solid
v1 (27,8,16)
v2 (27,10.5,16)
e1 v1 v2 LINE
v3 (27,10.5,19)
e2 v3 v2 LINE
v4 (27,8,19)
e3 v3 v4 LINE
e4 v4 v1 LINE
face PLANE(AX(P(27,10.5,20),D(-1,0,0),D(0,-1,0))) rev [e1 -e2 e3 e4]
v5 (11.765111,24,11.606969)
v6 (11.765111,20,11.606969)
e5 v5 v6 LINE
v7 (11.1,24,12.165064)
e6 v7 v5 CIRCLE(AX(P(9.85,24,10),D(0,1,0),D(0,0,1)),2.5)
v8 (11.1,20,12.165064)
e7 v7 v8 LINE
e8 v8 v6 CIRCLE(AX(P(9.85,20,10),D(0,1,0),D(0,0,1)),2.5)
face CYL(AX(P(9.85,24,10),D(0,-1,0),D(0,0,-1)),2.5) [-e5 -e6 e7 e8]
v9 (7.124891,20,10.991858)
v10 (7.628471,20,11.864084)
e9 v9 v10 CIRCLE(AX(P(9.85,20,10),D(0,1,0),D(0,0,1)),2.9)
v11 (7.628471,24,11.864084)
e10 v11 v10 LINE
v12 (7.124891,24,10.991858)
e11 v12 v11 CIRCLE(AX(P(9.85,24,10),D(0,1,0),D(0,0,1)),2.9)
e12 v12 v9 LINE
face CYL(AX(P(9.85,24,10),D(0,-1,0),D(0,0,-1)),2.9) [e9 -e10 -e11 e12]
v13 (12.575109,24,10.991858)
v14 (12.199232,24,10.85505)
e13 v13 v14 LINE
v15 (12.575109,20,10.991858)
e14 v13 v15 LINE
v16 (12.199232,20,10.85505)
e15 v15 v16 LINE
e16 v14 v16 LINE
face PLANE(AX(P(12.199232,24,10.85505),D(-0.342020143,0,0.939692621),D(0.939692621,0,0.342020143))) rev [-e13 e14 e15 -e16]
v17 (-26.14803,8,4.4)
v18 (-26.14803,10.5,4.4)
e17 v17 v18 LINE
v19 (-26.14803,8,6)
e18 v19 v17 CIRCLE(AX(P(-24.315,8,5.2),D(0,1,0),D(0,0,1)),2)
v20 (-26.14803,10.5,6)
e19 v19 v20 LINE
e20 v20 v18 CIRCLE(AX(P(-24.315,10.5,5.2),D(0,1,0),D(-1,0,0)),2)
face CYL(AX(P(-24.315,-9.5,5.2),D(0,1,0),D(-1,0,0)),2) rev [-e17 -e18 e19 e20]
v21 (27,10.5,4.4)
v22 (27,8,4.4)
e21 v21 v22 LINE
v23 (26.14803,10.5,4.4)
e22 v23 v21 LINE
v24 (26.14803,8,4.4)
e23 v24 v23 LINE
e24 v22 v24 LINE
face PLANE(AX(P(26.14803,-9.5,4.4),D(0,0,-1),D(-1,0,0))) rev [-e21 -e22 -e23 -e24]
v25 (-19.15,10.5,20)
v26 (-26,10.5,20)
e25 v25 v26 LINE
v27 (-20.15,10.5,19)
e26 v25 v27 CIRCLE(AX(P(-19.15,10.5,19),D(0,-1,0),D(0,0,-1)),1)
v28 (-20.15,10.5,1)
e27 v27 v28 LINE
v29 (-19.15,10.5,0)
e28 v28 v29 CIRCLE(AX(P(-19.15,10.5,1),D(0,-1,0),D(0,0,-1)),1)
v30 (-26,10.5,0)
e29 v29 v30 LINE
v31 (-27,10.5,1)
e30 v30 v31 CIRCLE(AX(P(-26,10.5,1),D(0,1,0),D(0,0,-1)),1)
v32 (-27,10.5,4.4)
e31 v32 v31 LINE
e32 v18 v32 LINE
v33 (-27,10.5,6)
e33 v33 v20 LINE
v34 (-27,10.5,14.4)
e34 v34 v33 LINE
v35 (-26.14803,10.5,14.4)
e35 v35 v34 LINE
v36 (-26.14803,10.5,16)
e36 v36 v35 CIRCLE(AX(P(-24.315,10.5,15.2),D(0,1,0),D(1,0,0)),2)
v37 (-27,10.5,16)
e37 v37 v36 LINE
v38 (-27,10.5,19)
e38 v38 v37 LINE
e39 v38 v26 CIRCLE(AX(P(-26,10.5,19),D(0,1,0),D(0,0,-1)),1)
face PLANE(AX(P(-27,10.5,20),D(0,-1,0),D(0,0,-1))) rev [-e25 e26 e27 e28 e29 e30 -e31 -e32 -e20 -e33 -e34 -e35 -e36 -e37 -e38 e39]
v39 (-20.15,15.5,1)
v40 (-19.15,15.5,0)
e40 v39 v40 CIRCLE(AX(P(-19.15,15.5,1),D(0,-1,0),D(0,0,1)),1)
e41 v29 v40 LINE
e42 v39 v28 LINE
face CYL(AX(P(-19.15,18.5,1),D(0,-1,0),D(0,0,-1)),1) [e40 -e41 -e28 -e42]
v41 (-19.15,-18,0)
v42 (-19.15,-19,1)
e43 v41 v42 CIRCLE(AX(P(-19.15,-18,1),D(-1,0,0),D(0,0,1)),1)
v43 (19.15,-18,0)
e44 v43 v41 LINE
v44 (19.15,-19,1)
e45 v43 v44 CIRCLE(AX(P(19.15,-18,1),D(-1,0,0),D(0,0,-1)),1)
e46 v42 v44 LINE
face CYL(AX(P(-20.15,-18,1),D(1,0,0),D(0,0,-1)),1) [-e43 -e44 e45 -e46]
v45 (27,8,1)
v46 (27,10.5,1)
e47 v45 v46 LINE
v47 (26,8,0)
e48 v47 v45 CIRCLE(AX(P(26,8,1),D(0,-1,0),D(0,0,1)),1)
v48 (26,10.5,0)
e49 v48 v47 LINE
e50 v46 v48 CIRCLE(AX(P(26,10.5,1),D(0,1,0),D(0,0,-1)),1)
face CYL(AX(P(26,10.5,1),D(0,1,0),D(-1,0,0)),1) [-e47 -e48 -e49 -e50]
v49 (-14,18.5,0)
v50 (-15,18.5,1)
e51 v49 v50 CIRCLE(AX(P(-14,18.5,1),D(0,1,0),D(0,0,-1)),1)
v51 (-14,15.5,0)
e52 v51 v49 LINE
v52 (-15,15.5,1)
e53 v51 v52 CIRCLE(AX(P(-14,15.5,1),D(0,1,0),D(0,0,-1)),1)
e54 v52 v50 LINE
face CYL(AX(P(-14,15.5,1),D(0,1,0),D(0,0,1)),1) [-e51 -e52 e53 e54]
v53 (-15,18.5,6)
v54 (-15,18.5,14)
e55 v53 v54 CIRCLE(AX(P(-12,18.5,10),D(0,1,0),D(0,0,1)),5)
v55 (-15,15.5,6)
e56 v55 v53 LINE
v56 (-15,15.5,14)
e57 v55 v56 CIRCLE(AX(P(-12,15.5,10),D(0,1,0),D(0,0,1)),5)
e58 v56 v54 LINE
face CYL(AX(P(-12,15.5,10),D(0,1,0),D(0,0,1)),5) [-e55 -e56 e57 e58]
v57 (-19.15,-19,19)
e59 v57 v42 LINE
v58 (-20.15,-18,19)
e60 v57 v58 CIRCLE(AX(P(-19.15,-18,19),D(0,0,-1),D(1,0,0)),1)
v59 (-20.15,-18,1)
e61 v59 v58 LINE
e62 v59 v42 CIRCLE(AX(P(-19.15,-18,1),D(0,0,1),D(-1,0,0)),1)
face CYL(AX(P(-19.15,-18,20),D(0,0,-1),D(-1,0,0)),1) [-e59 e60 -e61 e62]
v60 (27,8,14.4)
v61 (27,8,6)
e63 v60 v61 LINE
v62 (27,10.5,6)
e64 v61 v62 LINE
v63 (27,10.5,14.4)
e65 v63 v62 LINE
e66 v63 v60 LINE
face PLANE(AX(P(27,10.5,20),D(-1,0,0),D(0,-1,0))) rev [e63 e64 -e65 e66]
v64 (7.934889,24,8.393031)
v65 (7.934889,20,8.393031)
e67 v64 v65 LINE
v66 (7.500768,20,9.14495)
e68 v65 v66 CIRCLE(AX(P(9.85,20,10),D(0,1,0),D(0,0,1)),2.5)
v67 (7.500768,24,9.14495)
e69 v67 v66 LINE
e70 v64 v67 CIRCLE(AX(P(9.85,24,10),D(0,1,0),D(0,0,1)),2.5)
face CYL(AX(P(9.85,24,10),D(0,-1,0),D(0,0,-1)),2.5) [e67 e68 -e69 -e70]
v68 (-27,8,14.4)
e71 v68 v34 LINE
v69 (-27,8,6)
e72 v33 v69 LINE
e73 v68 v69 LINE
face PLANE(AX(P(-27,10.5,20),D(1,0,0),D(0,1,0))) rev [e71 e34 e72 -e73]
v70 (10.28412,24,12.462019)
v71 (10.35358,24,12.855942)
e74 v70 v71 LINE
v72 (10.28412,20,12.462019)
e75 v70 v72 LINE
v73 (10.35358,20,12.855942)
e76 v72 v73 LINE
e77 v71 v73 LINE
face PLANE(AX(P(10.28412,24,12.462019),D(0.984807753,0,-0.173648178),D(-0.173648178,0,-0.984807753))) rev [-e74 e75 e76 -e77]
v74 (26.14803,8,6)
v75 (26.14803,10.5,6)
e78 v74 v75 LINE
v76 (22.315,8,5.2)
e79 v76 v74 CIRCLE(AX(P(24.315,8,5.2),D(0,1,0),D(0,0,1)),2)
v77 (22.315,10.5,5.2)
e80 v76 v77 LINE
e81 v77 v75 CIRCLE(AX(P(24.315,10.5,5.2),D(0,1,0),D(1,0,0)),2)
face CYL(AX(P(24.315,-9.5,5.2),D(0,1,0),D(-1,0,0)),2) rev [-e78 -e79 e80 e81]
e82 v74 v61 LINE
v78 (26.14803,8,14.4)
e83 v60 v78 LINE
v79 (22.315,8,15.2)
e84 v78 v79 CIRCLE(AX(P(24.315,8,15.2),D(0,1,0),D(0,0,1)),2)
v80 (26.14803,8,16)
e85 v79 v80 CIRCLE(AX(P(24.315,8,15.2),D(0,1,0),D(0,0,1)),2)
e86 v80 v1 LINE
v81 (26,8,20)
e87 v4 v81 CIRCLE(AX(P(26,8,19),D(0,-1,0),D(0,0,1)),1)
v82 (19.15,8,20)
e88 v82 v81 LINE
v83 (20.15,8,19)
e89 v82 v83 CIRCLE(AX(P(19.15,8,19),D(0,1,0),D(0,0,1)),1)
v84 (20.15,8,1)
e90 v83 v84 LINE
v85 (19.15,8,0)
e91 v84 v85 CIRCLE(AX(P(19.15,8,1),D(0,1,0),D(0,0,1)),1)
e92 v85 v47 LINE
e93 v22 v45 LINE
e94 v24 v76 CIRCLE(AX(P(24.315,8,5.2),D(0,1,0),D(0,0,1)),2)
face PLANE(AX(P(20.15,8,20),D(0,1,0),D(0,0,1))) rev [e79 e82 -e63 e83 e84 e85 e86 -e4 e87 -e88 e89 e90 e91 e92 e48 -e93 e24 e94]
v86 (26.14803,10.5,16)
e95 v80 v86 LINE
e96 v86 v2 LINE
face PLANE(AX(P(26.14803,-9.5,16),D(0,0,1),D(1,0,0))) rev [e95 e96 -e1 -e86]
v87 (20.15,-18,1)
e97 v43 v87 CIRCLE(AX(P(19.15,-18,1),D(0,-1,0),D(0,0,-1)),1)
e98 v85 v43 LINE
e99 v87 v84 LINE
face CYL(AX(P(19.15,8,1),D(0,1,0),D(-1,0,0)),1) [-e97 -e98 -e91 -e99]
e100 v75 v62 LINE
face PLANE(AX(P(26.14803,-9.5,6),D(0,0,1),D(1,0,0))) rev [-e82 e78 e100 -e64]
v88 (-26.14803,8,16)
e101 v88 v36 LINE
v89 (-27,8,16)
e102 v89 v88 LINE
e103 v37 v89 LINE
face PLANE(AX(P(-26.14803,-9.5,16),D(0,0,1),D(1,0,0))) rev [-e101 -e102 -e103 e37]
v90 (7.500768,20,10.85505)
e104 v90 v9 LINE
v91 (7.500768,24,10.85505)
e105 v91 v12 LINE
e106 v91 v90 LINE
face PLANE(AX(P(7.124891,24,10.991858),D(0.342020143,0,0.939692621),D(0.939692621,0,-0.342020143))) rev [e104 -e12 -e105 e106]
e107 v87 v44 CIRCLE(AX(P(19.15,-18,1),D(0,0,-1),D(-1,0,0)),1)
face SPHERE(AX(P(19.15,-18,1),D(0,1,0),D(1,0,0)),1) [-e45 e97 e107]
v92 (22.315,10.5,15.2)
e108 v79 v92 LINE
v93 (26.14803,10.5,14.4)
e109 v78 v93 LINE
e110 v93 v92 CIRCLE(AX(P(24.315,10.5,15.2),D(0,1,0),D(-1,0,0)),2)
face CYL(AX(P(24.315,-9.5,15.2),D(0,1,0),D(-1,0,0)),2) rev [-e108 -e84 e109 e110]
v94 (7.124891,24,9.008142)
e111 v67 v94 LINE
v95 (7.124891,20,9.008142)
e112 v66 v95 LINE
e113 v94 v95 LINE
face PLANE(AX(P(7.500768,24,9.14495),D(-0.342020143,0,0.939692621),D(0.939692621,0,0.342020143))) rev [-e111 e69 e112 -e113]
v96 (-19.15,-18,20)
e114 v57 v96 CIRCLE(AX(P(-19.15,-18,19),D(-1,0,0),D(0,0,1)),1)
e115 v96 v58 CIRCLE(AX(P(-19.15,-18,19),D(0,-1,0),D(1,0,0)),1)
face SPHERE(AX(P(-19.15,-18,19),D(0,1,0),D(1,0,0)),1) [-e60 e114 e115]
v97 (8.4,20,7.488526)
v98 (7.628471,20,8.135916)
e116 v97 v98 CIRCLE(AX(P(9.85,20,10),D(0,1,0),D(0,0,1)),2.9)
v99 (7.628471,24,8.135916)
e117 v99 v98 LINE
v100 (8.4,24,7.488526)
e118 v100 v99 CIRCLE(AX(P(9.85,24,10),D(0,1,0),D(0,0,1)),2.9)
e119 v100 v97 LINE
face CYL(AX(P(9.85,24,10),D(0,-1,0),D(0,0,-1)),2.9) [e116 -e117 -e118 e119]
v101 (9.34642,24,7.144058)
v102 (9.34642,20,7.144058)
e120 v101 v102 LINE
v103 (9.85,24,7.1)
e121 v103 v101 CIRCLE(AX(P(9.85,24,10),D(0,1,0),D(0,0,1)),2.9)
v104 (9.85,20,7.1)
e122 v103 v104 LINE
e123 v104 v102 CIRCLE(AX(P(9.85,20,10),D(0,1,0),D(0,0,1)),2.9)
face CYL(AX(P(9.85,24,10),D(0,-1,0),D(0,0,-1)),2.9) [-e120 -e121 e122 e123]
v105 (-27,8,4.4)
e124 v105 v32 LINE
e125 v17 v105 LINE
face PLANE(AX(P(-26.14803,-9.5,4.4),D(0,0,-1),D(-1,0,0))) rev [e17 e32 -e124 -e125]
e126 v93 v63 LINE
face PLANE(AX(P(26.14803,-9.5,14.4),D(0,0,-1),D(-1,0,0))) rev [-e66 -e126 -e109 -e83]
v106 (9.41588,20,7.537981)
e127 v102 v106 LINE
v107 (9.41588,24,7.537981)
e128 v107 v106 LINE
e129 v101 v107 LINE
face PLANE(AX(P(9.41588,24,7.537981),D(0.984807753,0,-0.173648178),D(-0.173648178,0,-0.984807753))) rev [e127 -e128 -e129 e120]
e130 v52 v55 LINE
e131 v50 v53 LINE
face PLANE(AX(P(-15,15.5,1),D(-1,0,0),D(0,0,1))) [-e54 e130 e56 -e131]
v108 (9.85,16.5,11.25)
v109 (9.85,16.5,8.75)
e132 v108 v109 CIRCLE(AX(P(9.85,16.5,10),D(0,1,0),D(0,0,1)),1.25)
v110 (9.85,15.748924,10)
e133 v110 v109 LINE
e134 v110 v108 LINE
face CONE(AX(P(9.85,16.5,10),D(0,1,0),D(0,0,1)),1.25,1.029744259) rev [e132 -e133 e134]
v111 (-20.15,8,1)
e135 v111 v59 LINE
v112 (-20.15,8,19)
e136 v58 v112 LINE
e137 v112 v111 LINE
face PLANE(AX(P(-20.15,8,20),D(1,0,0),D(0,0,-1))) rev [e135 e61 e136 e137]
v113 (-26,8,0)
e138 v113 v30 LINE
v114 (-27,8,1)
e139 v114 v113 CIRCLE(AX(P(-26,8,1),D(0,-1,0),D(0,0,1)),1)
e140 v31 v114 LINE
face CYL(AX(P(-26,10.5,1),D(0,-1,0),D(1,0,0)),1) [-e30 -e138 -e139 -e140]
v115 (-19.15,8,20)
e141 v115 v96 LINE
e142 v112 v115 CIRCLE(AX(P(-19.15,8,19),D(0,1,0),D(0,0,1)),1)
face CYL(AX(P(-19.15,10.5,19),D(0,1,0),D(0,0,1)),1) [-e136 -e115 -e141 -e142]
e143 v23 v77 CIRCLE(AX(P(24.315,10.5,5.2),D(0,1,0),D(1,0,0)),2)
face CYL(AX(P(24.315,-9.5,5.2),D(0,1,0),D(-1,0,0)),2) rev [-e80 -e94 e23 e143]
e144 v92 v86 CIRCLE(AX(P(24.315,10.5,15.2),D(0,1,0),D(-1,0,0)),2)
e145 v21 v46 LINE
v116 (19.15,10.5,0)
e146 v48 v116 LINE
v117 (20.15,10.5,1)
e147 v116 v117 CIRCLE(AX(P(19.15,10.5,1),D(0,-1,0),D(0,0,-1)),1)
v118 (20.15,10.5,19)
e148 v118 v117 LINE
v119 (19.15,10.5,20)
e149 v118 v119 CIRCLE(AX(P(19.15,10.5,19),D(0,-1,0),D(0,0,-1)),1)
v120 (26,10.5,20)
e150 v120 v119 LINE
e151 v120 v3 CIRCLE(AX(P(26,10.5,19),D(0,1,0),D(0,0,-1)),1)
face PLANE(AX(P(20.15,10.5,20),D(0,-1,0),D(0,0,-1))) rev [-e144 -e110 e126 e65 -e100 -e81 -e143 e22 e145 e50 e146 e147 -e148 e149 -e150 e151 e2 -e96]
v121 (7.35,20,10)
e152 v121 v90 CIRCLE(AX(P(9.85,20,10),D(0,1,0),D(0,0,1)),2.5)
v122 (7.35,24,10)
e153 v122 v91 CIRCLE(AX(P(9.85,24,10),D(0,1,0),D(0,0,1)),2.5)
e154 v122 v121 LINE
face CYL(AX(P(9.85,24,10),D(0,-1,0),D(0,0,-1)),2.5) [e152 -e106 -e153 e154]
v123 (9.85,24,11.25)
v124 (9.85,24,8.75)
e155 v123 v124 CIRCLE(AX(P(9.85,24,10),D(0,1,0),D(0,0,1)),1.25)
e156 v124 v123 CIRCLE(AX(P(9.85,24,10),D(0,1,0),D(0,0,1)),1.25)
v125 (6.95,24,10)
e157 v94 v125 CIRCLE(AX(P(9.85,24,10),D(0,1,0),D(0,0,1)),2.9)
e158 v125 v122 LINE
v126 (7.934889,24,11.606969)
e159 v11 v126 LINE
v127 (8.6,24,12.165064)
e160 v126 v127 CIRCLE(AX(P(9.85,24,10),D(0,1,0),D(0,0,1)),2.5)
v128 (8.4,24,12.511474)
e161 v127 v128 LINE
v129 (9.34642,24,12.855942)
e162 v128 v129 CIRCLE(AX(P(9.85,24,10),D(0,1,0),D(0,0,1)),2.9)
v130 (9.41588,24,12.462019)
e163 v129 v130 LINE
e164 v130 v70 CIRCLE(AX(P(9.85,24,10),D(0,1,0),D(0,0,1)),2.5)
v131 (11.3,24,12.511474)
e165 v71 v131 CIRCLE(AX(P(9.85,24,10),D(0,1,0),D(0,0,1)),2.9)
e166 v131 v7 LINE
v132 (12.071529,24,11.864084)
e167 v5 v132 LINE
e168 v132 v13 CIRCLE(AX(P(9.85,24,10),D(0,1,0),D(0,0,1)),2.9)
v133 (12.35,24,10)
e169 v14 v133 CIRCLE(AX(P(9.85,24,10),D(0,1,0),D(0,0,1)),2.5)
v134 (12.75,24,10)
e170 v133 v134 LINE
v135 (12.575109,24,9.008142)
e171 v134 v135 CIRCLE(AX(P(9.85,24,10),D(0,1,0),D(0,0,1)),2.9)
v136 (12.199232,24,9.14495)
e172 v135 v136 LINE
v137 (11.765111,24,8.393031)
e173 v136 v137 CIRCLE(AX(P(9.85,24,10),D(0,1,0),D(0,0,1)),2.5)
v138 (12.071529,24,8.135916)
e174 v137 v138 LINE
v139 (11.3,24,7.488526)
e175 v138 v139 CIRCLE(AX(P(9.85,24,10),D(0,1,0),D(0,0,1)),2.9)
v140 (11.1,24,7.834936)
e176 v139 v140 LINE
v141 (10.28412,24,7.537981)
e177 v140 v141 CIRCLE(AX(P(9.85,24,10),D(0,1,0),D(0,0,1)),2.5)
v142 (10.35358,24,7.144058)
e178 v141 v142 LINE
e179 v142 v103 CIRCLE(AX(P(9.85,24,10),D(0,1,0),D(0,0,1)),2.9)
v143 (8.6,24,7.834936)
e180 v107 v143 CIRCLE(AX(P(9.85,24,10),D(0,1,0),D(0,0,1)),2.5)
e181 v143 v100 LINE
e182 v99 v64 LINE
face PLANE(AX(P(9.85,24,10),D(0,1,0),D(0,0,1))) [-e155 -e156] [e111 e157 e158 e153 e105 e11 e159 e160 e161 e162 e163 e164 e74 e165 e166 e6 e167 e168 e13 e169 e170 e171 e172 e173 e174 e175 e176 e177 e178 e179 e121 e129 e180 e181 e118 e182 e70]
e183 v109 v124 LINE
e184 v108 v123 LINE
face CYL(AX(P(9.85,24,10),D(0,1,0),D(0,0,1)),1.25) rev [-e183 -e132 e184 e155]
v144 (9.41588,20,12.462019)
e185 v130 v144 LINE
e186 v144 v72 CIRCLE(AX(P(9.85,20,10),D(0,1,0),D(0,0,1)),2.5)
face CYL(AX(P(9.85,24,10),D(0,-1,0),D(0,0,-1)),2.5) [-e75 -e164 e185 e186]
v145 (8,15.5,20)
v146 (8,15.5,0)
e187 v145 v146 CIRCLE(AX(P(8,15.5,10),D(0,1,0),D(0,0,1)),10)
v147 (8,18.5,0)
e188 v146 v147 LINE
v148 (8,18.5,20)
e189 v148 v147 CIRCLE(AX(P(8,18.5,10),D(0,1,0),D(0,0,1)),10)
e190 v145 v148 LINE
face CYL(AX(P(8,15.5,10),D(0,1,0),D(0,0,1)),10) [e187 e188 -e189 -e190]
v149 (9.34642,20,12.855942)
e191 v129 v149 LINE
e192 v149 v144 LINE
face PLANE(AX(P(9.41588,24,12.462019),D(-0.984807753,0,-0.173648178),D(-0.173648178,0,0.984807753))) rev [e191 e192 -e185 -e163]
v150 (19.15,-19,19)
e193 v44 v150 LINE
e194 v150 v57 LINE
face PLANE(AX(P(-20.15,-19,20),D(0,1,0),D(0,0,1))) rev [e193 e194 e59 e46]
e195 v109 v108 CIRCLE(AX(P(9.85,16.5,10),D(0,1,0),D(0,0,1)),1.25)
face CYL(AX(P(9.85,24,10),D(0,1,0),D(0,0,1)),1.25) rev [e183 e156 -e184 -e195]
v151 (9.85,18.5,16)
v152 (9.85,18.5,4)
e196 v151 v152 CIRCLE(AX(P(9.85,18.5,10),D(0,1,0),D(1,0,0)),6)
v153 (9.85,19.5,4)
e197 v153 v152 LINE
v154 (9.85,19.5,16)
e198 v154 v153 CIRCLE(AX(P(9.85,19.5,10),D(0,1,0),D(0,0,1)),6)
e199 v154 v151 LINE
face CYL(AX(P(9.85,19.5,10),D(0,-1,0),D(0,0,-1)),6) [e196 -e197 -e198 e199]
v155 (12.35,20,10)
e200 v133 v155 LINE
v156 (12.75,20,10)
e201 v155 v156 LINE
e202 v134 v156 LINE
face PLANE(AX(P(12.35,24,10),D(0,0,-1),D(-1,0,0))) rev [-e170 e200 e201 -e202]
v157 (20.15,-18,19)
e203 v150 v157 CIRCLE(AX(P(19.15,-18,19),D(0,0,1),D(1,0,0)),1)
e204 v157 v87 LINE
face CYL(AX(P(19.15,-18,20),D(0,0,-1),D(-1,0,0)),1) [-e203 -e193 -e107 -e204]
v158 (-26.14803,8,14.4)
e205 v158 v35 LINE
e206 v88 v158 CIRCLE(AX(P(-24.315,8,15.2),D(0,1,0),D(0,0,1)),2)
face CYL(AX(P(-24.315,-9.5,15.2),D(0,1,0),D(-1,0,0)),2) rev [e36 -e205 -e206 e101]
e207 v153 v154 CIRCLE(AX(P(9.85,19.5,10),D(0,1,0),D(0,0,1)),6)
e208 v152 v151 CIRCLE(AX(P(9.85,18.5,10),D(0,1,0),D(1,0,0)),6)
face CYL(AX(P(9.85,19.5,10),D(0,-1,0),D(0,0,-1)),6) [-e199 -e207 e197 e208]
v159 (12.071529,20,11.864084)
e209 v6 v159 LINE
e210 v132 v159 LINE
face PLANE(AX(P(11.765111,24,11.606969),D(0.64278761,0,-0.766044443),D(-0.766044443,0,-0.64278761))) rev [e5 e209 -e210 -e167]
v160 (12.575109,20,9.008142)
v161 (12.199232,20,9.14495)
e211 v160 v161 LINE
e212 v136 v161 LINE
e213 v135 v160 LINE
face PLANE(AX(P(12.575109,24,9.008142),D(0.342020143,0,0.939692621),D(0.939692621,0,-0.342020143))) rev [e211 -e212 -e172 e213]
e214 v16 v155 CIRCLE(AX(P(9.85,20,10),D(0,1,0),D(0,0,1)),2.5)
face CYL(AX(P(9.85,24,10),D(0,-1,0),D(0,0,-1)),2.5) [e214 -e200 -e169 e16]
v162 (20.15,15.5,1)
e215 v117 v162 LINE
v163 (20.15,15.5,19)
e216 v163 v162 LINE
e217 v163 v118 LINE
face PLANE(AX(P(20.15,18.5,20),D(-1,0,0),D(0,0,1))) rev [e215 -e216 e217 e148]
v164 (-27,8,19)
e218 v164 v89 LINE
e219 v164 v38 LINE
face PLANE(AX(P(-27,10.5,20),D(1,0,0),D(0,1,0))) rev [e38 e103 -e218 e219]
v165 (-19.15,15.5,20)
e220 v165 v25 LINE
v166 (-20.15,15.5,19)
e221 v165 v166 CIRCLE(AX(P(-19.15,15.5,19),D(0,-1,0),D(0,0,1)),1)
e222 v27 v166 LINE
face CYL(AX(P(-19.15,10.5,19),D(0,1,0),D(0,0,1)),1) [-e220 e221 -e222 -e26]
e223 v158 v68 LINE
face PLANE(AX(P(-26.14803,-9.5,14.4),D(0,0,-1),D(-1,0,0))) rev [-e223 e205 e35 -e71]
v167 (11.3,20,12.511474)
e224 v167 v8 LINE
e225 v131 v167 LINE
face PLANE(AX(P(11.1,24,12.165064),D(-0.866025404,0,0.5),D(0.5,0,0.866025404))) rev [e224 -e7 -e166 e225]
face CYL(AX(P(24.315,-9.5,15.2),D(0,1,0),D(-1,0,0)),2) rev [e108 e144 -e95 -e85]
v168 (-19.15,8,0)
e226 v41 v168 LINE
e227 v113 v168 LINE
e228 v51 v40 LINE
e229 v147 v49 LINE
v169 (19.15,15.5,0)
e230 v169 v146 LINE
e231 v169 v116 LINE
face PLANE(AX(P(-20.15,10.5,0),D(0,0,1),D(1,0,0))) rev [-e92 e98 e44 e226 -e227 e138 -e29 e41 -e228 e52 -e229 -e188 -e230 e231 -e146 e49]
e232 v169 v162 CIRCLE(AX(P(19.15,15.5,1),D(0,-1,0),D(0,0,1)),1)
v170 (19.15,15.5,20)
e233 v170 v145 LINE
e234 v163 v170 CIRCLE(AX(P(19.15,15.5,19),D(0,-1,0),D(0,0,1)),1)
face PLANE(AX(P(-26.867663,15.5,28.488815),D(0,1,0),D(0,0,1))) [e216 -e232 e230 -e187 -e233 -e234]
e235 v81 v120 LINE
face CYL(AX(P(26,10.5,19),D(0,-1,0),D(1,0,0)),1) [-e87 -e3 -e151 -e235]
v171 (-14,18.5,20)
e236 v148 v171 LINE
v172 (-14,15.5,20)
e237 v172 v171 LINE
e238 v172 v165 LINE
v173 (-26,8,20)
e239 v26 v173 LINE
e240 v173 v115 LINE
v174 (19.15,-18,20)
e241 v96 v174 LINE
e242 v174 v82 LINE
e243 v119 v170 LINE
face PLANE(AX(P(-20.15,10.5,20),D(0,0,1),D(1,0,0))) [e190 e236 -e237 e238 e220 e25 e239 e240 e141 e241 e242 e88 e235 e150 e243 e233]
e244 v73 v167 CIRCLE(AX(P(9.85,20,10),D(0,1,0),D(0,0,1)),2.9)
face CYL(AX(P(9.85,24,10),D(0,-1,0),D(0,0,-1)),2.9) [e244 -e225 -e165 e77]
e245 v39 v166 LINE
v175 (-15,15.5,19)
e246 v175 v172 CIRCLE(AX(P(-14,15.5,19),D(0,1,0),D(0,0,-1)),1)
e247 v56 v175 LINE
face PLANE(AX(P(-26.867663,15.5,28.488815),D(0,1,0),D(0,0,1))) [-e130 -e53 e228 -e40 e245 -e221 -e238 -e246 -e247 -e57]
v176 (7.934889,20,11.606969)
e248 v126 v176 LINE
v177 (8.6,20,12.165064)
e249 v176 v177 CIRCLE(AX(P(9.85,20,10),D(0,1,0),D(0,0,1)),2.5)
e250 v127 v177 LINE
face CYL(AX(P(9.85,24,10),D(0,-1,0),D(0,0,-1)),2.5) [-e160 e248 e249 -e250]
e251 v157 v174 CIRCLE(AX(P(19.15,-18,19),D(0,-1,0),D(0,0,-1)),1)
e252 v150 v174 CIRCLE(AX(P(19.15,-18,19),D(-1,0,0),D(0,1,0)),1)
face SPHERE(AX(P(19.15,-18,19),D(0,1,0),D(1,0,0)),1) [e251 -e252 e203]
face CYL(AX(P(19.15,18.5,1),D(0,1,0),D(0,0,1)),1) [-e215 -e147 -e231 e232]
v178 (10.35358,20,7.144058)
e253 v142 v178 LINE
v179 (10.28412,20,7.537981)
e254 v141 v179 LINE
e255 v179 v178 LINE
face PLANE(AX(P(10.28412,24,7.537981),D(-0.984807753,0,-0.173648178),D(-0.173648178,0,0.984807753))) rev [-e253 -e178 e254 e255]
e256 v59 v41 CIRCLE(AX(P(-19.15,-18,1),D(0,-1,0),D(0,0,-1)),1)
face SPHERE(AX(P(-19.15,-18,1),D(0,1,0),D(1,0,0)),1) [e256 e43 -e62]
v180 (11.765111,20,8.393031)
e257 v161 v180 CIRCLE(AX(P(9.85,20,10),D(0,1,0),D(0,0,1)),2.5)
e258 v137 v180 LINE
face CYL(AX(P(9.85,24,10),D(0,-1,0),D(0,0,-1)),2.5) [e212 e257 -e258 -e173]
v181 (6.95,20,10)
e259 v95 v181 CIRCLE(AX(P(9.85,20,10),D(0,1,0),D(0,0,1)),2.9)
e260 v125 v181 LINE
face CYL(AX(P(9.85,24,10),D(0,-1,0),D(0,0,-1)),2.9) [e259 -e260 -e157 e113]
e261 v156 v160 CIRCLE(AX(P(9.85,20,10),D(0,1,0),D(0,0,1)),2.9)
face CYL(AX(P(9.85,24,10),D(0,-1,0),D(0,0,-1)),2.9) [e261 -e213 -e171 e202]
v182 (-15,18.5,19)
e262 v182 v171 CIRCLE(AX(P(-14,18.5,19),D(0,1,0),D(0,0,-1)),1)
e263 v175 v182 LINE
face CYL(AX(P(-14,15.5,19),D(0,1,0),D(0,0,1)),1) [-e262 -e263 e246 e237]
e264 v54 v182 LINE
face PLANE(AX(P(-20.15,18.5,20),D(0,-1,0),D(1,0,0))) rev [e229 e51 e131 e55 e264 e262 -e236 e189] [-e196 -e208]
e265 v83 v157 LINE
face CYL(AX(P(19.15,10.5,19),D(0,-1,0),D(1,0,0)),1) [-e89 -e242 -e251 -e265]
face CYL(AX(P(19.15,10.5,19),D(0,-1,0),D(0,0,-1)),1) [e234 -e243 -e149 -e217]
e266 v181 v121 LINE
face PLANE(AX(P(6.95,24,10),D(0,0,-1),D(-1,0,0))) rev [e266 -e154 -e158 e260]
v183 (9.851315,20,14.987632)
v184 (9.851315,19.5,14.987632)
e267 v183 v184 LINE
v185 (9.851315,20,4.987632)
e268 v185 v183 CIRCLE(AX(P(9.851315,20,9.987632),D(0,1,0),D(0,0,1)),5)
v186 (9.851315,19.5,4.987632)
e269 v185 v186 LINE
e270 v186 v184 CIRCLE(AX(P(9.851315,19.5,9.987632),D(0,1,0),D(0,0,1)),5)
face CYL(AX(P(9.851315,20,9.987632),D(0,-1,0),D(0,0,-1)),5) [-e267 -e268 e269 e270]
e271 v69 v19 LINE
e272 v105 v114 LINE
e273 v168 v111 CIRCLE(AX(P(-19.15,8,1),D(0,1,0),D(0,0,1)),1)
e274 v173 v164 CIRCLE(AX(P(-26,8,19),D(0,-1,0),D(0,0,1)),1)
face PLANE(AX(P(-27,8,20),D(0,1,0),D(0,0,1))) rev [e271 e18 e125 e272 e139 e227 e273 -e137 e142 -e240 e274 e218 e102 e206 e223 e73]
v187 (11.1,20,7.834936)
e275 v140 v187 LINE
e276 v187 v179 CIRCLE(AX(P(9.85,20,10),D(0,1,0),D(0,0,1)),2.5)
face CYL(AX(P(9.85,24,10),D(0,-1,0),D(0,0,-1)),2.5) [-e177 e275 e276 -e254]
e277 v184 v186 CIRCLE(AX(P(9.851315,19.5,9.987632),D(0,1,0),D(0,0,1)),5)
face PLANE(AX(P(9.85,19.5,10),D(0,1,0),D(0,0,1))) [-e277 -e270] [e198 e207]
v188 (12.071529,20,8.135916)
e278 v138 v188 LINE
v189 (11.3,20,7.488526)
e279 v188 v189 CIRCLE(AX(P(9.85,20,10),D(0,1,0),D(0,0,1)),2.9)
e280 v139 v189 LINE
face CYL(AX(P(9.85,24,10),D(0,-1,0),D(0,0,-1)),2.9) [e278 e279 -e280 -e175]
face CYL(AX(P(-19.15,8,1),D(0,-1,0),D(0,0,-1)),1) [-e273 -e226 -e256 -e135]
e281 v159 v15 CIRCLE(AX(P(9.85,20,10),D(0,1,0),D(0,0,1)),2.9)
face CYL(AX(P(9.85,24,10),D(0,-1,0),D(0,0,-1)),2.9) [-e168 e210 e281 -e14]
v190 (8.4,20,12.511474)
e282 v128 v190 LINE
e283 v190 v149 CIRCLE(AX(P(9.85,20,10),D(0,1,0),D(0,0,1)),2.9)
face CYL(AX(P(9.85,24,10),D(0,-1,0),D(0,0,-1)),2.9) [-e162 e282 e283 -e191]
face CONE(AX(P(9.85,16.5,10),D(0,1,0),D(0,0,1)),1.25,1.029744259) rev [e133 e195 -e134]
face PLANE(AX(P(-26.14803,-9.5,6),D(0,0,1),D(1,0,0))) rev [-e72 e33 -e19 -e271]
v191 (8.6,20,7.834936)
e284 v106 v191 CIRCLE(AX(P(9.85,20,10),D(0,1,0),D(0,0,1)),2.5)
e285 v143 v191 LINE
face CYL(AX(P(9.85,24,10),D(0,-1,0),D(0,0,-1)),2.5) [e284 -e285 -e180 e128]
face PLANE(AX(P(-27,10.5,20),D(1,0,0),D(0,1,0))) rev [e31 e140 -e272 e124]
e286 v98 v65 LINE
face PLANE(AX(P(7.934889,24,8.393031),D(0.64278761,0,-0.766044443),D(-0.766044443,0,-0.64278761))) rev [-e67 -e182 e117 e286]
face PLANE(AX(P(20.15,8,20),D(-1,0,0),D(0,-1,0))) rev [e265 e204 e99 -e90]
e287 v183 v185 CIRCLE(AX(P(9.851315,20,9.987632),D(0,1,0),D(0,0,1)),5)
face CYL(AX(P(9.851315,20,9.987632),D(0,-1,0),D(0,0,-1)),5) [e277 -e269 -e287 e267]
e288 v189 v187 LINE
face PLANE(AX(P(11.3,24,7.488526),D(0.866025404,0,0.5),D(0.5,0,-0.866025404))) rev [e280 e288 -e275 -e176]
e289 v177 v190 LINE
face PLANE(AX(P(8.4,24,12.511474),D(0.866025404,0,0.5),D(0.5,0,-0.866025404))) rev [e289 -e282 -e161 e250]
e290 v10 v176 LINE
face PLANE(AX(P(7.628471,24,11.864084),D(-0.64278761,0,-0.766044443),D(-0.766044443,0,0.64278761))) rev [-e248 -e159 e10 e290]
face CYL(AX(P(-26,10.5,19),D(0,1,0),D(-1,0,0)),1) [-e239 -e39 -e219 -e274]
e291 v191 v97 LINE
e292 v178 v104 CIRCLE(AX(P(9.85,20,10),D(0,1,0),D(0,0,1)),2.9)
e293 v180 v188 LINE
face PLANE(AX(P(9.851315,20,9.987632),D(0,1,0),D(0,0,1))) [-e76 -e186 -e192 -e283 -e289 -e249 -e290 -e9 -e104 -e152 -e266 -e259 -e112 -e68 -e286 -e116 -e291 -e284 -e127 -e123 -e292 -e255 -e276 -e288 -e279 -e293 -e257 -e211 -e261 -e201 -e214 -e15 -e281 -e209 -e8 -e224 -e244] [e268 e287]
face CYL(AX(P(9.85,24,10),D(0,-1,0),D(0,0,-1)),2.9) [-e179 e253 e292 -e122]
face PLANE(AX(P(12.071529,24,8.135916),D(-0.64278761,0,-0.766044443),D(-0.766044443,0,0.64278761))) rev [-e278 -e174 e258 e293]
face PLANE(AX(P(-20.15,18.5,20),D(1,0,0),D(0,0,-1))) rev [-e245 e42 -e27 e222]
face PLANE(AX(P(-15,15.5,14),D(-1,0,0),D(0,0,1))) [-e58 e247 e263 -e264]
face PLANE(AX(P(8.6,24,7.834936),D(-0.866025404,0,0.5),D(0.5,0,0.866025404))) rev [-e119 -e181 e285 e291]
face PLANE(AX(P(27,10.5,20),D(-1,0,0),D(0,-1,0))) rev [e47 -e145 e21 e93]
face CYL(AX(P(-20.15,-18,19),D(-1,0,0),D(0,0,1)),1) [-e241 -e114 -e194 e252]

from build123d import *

# Parameters (mm, degrees)
BOSS_EXTRUDE1_DEPTH   = 20
FILLET1_R             = 1
CUT_EXTRUDE1_DEPTH    = 20
SKETCH3_W             = 51.867663345
SKETCH3_H             = 35.261757523
CUT_EXTRUDE2_DEPTH    = 3
SKETCH4_R             = 6
BOSS_EXTRUDE2_DEPTH   = 1
SKETCH5_R             = 5
BOSS_EXTRUDE3_DEPTH   = 0.5
SKETCH6_R             = 1
BOSS_EXTRUDE4_DEPTH   = 4
M3_TAPPED_HOLE1_D     = 2.5
M3_TAPPED_HOLE1_DEPTH = 7.5
M3_TAPPED_HOLE1_TIP   = 0.751075774


with BuildPart() as part:
    # Sketch1 → Boss-Extrude1 (new body)
    with BuildSketch(Plane.XY):
        Polygon((20.15, 8), (27, 8), (27, 10.5), (20.15, 10.5), (20.15, 18.5), (-20.15, 18.5), (-20.15, 10.5), (-27, 10.5), (-27, 8), (-20.15, 8), (-20.15, -19), (20.15, -19), align=None)
    extrude(amount=BOSS_EXTRUDE1_DEPTH)

    # Fillet1
    fillet1_edges = [part.edges().sort_by_distance(p)[0] for p in [
        (-27, 9.25, 20),
        (20.15, 14.5, 0),
        (27, 9.25, 0),
        (20.15, -5.5, 0),
        (0, -19, 0),
        (-20.15, -5.5, 0),
        (-27, 9.25, 0),
        (-20.15, 14.5, 0),
        (-20.15, -5.5, 20),
        (0, -19, 20),
        (-20.15, 18.5, 10),
        (20.15, 18.5, 10),
        (20.15, -19, 10),
        (-20.15, -19, 10),
        (20.15, -5.5, 20),
        (27, 9.25, 20),
        (20.15, 14.5, 20),
        (-20.15, 14.5, 20),
    ]]
    fillet(fillet1_edges, radius=FILLET1_R)

    # Sketch2 → Cut-Extrude1 (cut)
    with BuildSketch(Plane(origin=(0, 10.5, 0), x_dir=(1, 0, 0), z_dir=(0, 1, 0))):
        with BuildLine():
            Line((-26.148030278, -4.4), (-29.222738853, -4.4))
            Line((-29.222738853, -4.4), (-29.222738853, -6))
            Line((-29.222738853, -6), (-26.148030278, -6))
            ThreePointArc((-26.148030278, -6), (-22.315, -5.2), (-26.148030278, -4.4))
        make_face()
        with BuildLine():
            Line((-26.148030278, -14.4), (-29.222738853, -14.4))
            Line((-29.222738853, -14.4), (-29.222738853, -16))
            Line((-29.222738853, -16), (-26.148030278, -16))
            ThreePointArc((-26.148030278, -16), (-22.315, -15.2), (-26.148030278, -14.4))
        make_face()
        with BuildLine():
            Line((26.148030278, -16), (29.222738853, -16))
            Line((29.222738853, -16), (29.222738853, -14.4))
            Line((29.222738853, -14.4), (26.148030278, -14.4))
            ThreePointArc((26.148030278, -14.4), (22.315, -15.2), (26.148030278, -16))
        make_face()
        with BuildLine():
            Line((29.222738853, -4.4), (29.222738853, -6))
            Line((29.222738853, -6), (26.148030278, -6))
            ThreePointArc((26.148030278, -6), (22.315, -5.2), (26.148030278, -4.4))
            Line((26.148030278, -4.4), (29.222738853, -4.4))
        make_face()
    extrude(amount=-CUT_EXTRUDE1_DEPTH, mode=Mode.SUBTRACT)

    # Sketch3 → Cut-Extrude2 (cut)
    with BuildSketch(Plane(origin=(0, 18.5, 0), x_dir=(1, 0, 0), z_dir=(0, 1, 0))):
        with Locations((-0.933831673, -10.85793672)):
            Rectangle(SKETCH3_W, SKETCH3_H)
        with BuildLine():
            Line((-14, 0), (8, 0))
            ThreePointArc((8, 0), (18, -10), (8, -20))
            Line((8, -20), (-14, -20))
            ThreePointArc((-14, -20), (-14.707106781, -19.707106781), (-15, -19))
            Line((-15, -19), (-15, -14))
            ThreePointArc((-15, -14), (-17, -10), (-15, -6))
            Line((-15, -6), (-15, -1))
            ThreePointArc((-15, -1), (-14.707106781, -0.292893219), (-14, 0))
        make_face(mode=Mode.SUBTRACT)
    extrude(amount=-CUT_EXTRUDE2_DEPTH, mode=Mode.SUBTRACT)

    # Sketch4 → Boss-Extrude2 (add)
    with BuildSketch(Plane(origin=(0, 18.5, 0), x_dir=(1, 0, 0), z_dir=(0, 1, 0))):
        with Locations((9.85, -10)):
            Circle(SKETCH4_R)
    extrude(amount=BOSS_EXTRUDE2_DEPTH)

    # Sketch5 → Boss-Extrude3 (add)
    with BuildSketch(Plane(origin=(0, 19.5, 0), x_dir=(1, 0, 0), z_dir=(0, 1, 0))):
        with Locations(Location((9.851314919, -9.987632383, 0), (0, 0, 270))):
            Circle(SKETCH5_R)
    extrude(amount=BOSS_EXTRUDE3_DEPTH)

    # Sketch6 → Boss-Extrude4 (add)
    with BuildSketch(Plane(origin=(0, 20, 0), x_dir=(1, 0, 0), z_dir=(0, 1, 0))):
        with BuildLine():
            Line((10.284120444, -7.537980617), (10.353579715, -7.144057516))
            ThreePointArc((10.353579715, -7.144057516), (9.85, -7.1), (9.346420285, -7.144057516))
            Line((9.346420285, -7.144057516), (9.415879556, -7.537980617))
            ThreePointArc((9.415879556, -7.537980617), (8.994949642, -7.650768448), (8.6, -7.834936491))
            Line((8.6, -7.834936491), (8.4, -7.488526329))
            ThreePointArc((8.4, -7.488526329), (7.985915932, -7.778471115), (7.628471115, -8.135915932))
            Line((7.628471115, -8.135915932), (7.934888892, -8.393030976))
            ThreePointArc((7.934888892, -8.393030976), (7.684936491, -8.75), (7.500768448, -9.144949642))
            Line((7.500768448, -9.144949642), (7.1248914, -9.008141584))
            ThreePointArc((7.1248914, -9.008141584), (6.994057516, -9.496420285), (6.95, -10))
            Line((6.95, -10), (7.35, -10))
            ThreePointArc((7.35, -10), (7.387980617, -10.434120444), (7.500768448, -10.855050358))
            Line((7.500768448, -10.855050358), (7.1248914, -10.991858416))
            ThreePointArc((7.1248914, -10.991858416), (7.338526329, -11.45), (7.628471115, -11.864084068))
            Line((7.628471115, -11.864084068), (7.934888892, -11.606969024))
            ThreePointArc((7.934888892, -11.606969024), (8.243030976, -11.915111108), (8.6, -12.165063509))
            Line((8.6, -12.165063509), (8.4, -12.511473671))
            ThreePointArc((8.4, -12.511473671), (8.858141584, -12.7251086), (9.346420285, -12.855942484))
            Line((9.346420285, -12.855942484), (9.415879556, -12.462019383))
            ThreePointArc((9.415879556, -12.462019383), (9.85, -12.5), (10.284120444, -12.462019383))
            Line((10.284120444, -12.462019383), (10.353579715, -12.855942484))
            ThreePointArc((10.353579715, -12.855942484), (10.841858416, -12.7251086), (11.3, -12.511473671))
            Line((11.3, -12.511473671), (11.1, -12.165063509))
            ThreePointArc((11.1, -12.165063509), (11.456969024, -11.915111108), (11.765111108, -11.606969024))
            Line((11.765111108, -11.606969024), (12.071528885, -11.864084068))
            ThreePointArc((12.071528885, -11.864084068), (12.361473671, -11.45), (12.5751086, -10.991858416))
            Line((12.5751086, -10.991858416), (12.199231552, -10.855050358))
            ThreePointArc((12.199231552, -10.855050358), (12.312019383, -10.434120444), (12.35, -10))
            Line((12.35, -10), (12.75, -10))
            ThreePointArc((12.75, -10), (12.705942484, -9.496420285), (12.5751086, -9.008141584))
            Line((12.5751086, -9.008141584), (12.199231552, -9.144949642))
            ThreePointArc((12.199231552, -9.144949642), (12.015063509, -8.75), (11.765111108, -8.393030976))
            Line((11.765111108, -8.393030976), (12.071528885, -8.135915932))
            ThreePointArc((12.071528885, -8.135915932), (11.714084068, -7.778471115), (11.3, -7.488526329))
            Line((11.3, -7.488526329), (11.1, -7.834936491))
            ThreePointArc((11.1, -7.834936491), (10.705050358, -7.650768448), (10.284120444, -7.537980617))
        make_face()
        with Locations(Location((9.85, -10, 0), (0, 0, 270))):
            Circle(SKETCH6_R, mode=Mode.SUBTRACT)
    extrude(amount=BOSS_EXTRUDE4_DEPTH)

    # M3 Tapped Hole1
    with Locations(Plane(origin=(9.85, 24, 10), x_dir=(0, 0, 1), z_dir=(0, 1, 0))):
        with Locations((0, 0)):
            Hole(M3_TAPPED_HOLE1_D / 2, depth=M3_TAPPED_HOLE1_DEPTH)
            with Locations((0, 0, -(M3_TAPPED_HOLE1_DEPTH + M3_TAPPED_HOLE1_TIP / 2))):  # 118° drill point
                Cone(0, M3_TAPPED_HOLE1_D / 2, M3_TAPPED_HOLE1_TIP, mode=Mode.SUBTRACT)


solid = part.part
